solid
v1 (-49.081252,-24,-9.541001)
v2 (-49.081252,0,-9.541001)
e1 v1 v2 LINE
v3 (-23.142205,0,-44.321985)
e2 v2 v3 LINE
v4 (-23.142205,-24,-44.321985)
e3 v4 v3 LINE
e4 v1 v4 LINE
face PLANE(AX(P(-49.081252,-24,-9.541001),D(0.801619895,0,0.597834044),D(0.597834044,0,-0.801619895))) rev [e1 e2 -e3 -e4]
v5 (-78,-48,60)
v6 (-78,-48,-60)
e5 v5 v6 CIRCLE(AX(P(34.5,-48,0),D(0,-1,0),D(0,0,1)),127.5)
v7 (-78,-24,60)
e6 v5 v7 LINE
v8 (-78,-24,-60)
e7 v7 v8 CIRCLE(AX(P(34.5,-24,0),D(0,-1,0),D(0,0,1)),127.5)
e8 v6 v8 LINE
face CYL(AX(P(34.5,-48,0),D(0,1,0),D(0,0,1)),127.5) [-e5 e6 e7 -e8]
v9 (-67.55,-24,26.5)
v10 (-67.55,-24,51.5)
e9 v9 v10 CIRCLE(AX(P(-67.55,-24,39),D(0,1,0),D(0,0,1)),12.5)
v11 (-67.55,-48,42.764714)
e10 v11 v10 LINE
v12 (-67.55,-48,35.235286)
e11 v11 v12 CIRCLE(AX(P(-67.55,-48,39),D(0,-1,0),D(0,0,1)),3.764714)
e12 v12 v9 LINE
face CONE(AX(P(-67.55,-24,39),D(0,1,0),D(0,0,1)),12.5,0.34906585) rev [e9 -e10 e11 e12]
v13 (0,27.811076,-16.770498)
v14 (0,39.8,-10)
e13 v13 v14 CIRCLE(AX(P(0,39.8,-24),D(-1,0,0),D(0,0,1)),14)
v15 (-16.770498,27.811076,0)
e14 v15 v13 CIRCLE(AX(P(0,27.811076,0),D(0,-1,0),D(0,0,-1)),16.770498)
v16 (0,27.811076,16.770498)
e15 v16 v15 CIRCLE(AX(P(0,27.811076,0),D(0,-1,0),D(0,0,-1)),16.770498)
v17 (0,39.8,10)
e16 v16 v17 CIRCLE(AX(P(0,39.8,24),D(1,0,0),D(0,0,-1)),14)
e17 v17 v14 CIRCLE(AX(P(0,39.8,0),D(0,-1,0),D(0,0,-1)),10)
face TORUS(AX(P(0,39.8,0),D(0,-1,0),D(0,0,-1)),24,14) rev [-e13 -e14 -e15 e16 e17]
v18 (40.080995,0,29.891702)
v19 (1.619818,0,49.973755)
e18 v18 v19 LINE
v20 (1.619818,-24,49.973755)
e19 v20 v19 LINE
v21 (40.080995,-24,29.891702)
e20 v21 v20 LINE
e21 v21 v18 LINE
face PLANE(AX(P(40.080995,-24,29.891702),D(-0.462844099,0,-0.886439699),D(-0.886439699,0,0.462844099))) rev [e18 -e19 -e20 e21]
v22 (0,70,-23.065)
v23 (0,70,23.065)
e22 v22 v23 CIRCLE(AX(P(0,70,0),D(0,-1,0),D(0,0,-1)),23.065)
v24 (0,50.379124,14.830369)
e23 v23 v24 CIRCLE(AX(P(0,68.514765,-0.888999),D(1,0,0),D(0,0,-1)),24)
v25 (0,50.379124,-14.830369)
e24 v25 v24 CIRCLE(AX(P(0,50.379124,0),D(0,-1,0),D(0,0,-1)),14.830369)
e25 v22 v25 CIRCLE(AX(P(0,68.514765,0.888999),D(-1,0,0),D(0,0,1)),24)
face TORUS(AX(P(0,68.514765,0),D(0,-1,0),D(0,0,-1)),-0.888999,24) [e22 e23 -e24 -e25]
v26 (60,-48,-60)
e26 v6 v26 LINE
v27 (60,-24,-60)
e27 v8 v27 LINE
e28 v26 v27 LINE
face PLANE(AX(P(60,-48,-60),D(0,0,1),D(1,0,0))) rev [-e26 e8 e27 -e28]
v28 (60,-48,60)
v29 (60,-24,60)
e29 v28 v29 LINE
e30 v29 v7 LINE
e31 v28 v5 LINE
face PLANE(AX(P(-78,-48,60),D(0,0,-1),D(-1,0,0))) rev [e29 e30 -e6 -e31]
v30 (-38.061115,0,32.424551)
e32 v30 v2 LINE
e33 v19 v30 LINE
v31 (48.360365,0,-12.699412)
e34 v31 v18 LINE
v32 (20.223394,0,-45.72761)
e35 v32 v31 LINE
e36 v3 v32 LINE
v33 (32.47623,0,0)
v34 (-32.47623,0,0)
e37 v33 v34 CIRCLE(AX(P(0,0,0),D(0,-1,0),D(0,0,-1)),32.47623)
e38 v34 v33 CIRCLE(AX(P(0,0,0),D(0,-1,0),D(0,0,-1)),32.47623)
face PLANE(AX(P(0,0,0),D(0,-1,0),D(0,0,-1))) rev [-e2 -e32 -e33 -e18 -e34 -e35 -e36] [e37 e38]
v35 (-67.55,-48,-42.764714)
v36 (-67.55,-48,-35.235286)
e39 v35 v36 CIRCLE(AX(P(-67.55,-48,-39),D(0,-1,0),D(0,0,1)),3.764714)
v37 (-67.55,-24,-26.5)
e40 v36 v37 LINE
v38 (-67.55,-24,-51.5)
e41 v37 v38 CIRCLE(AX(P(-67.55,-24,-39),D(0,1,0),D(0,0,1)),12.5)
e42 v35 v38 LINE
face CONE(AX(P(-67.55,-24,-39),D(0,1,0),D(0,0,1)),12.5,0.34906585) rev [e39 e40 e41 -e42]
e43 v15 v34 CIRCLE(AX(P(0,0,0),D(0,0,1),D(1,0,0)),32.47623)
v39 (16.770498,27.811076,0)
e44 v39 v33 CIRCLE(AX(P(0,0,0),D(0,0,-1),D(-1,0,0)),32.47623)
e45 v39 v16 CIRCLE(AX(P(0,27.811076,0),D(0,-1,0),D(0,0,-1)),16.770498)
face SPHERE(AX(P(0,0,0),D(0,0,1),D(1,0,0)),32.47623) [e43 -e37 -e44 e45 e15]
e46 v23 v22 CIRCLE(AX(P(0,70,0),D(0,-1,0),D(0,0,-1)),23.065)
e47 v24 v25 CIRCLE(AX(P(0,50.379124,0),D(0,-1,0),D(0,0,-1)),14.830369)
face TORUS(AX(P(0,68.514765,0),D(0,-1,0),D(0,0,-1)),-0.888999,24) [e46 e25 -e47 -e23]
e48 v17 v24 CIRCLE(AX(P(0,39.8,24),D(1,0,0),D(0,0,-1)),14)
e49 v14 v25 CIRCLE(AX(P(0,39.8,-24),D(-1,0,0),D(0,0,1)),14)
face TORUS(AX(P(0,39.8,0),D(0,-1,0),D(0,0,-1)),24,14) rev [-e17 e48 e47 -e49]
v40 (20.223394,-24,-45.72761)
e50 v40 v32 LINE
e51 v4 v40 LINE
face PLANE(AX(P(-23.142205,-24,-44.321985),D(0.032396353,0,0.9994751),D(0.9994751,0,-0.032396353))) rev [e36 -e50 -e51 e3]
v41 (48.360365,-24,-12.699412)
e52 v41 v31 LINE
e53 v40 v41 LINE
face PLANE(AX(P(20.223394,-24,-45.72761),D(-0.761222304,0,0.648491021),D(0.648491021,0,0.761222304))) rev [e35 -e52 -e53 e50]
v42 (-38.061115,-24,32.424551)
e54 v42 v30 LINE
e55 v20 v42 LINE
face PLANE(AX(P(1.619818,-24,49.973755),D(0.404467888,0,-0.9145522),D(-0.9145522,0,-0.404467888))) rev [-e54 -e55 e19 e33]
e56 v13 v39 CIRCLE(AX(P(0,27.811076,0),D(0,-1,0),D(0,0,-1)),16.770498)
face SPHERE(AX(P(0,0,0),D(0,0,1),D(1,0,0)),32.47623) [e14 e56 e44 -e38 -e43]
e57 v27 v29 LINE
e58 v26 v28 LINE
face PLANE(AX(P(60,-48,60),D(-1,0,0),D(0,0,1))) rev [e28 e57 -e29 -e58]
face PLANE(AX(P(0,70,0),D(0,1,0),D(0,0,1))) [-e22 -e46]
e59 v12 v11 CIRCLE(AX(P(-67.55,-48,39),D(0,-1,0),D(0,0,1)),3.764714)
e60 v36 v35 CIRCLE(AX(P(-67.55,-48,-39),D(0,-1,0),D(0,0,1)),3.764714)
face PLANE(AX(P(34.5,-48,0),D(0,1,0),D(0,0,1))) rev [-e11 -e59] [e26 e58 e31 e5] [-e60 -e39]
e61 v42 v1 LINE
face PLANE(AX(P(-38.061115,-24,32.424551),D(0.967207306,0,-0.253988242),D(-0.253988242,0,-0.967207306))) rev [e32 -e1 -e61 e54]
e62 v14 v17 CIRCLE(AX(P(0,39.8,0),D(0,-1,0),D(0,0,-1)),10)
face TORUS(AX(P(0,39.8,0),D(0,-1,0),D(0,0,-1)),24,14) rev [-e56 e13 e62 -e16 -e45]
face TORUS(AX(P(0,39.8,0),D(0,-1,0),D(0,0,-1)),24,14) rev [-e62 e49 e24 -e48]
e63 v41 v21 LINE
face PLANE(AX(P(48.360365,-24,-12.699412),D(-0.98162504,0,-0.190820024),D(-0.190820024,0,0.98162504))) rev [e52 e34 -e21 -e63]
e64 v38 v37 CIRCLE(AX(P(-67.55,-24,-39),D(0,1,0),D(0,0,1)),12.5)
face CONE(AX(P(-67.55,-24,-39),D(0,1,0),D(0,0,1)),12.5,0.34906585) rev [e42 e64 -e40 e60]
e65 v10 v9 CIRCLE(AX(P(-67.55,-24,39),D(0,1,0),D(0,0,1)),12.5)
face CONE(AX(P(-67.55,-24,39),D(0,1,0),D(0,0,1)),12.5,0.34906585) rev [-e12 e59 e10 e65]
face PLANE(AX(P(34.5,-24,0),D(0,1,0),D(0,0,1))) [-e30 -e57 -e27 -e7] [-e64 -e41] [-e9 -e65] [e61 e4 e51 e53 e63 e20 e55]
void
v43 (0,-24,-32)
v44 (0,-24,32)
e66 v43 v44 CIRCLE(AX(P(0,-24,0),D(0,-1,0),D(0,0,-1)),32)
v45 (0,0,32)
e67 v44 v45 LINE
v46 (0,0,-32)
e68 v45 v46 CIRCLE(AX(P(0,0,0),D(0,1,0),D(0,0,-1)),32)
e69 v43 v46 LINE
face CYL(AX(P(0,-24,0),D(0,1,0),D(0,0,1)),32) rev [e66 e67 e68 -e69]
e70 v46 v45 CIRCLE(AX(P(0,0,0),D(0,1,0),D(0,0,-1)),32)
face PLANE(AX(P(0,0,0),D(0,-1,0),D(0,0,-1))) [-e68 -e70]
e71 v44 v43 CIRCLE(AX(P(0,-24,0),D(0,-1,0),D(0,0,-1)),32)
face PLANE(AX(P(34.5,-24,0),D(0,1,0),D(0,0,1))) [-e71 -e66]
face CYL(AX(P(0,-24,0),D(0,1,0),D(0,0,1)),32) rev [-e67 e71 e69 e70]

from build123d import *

# Parameters (mm, degrees)
HEX_BOSS_SKETCH_R                 = 32
HEX_BOSS_DEPTH                    = 24
BASE_PLATE_DEPTH                  = 24
PLATE_HOLES_SKETCH_R              = 12.5
PLATE_HOLES_2X_25_DEPTH           = 24
PLATE_HOLES_2X_25_DRAFT           = -20
PLATE_HOLES_2X_25_PROFILE_2_DEPTH = 24
PLATE_HOLES_2X_25_PROFILE_2_DRAFT = -20


with BuildPart() as part:
    # Knob Profile Sketch → Ball Knob (revolve)
    with BuildSketch(Plane.XY, mode=Mode.PRIVATE) as ball_knob_sk:
        with BuildLine():
            Line((0, 0), (0, 70))
            Line((0, 70), (23.065, 70))
            ThreePointArc((23.065, 70), (21.241041688, 59.227069146), (14.830368725, 50.37912389))
            ThreePointArc((14.830368725, 50.37912389), (10.051448448, 38.600871321), (16.770498027, 27.811075894))
            ThreePointArc((16.770498027, 27.811075894), (28.278508674, 15.969705495), (32.476230484, 0))
            Line((32.476230484, 0), (0, 0))
        make_face()
    revolve(ball_knob_sk.sketch.rotate(Axis((0, 0, 0), (0, 1, 0)), 90), axis=Axis((0, 0, 0), (0, 1, 0)))

    # Hex Boss Sketch → Hex Boss (add)
    with BuildSketch(Plane.XZ):
        Polygon((1.619817649, 49.97375502), (-38.061115187, 32.424551049), (-49.081251981, -9.541001202), (-23.142204959, -44.321984947), (20.223394412, -45.727610023), (48.360365309, -12.699412079), (40.080994757, 29.891702182), align=None)
        with Locations(Location((0, 0, 0), (0, 0, 270))):
            Circle(HEX_BOSS_SKETCH_R, mode=Mode.SUBTRACT)
    extrude(amount=HEX_BOSS_DEPTH)

    # Base Plate Sketch → Base Plate (add)
    with BuildSketch(Plane.XZ.offset(24)):
        with BuildLine():
            Line((-78, 60), (60, 60))
            Line((60, 60), (60, -60))
            Line((60, -60), (-78, -60))
            ThreePointArc((-78, -60), (-93, 0), (-78, 60))
        make_face()
    extrude(amount=BASE_PLATE_DEPTH)


with BuildPart() as plate_holes_2x_25_tool:
    # Plate Holes Sketch → Plate Holes 2xØ25 (with draft: the straight prism first)
    with BuildSketch(Plane(origin=(0, -24, 0), x_dir=(1, 0, 0), z_dir=(0, 1, 0))):
        with Locations((-67.55, 39)):
            Circle(PLATE_HOLES_SKETCH_R)
    extrude(amount=-PLATE_HOLES_2X_25_DEPTH)
    # Plate Holes 2xØ25: the draft: its side faces are tilted about the plane it starts from
    plate_holes_2x_25_sides = [plate_holes_2x_25_tool.faces().sort_by_distance(p)[0] for p in [
        (-80.05, -36, -39),
    ]]
    draft(plate_holes_2x_25_sides, Plane(origin=(0, -24, 0), x_dir=(1, 0, 0), z_dir=(0, 1, 0)), PLATE_HOLES_2X_25_DRAFT)


with BuildPart() as part_1:
    add(part.part)

    # Plate Holes 2xØ25: cut by plate_holes_2x_25_tool
    add(plate_holes_2x_25_tool.part, mode=Mode.SUBTRACT)


with BuildPart() as plate_holes_2x_25_profile_2_tool:
    # Plate Holes Sketch → Plate Holes 2xØ25 profile 2 (with draft: the straight prism first)
    with BuildSketch(Plane(origin=(0, -24, 0), x_dir=(1, 0, 0), z_dir=(0, 1, 0))):
        with Locations((-67.55, -39)):
            Circle(PLATE_HOLES_SKETCH_R)
    extrude(amount=-PLATE_HOLES_2X_25_PROFILE_2_DEPTH)
    # Plate Holes 2xØ25 profile 2: the draft: its side faces are tilted about the plane it starts from
    plate_holes_2x_25_profile_2_sides = [plate_holes_2x_25_profile_2_tool.faces().sort_by_distance(p)[0] for p in [
        (-80.05, -36, 39),
    ]]
    draft(plate_holes_2x_25_profile_2_sides, Plane(origin=(0, -24, 0), x_dir=(1, 0, 0), z_dir=(0, 1, 0)), PLATE_HOLES_2X_25_PROFILE_2_DRAFT)


with BuildPart() as part_2:
    add(part_1.part)

    # Plate Holes 2xØ25 profile 2: cut by plate_holes_2x_25_profile_2_tool
    add(plate_holes_2x_25_profile_2_tool.part, mode=Mode.SUBTRACT)


solid = part_2.part
